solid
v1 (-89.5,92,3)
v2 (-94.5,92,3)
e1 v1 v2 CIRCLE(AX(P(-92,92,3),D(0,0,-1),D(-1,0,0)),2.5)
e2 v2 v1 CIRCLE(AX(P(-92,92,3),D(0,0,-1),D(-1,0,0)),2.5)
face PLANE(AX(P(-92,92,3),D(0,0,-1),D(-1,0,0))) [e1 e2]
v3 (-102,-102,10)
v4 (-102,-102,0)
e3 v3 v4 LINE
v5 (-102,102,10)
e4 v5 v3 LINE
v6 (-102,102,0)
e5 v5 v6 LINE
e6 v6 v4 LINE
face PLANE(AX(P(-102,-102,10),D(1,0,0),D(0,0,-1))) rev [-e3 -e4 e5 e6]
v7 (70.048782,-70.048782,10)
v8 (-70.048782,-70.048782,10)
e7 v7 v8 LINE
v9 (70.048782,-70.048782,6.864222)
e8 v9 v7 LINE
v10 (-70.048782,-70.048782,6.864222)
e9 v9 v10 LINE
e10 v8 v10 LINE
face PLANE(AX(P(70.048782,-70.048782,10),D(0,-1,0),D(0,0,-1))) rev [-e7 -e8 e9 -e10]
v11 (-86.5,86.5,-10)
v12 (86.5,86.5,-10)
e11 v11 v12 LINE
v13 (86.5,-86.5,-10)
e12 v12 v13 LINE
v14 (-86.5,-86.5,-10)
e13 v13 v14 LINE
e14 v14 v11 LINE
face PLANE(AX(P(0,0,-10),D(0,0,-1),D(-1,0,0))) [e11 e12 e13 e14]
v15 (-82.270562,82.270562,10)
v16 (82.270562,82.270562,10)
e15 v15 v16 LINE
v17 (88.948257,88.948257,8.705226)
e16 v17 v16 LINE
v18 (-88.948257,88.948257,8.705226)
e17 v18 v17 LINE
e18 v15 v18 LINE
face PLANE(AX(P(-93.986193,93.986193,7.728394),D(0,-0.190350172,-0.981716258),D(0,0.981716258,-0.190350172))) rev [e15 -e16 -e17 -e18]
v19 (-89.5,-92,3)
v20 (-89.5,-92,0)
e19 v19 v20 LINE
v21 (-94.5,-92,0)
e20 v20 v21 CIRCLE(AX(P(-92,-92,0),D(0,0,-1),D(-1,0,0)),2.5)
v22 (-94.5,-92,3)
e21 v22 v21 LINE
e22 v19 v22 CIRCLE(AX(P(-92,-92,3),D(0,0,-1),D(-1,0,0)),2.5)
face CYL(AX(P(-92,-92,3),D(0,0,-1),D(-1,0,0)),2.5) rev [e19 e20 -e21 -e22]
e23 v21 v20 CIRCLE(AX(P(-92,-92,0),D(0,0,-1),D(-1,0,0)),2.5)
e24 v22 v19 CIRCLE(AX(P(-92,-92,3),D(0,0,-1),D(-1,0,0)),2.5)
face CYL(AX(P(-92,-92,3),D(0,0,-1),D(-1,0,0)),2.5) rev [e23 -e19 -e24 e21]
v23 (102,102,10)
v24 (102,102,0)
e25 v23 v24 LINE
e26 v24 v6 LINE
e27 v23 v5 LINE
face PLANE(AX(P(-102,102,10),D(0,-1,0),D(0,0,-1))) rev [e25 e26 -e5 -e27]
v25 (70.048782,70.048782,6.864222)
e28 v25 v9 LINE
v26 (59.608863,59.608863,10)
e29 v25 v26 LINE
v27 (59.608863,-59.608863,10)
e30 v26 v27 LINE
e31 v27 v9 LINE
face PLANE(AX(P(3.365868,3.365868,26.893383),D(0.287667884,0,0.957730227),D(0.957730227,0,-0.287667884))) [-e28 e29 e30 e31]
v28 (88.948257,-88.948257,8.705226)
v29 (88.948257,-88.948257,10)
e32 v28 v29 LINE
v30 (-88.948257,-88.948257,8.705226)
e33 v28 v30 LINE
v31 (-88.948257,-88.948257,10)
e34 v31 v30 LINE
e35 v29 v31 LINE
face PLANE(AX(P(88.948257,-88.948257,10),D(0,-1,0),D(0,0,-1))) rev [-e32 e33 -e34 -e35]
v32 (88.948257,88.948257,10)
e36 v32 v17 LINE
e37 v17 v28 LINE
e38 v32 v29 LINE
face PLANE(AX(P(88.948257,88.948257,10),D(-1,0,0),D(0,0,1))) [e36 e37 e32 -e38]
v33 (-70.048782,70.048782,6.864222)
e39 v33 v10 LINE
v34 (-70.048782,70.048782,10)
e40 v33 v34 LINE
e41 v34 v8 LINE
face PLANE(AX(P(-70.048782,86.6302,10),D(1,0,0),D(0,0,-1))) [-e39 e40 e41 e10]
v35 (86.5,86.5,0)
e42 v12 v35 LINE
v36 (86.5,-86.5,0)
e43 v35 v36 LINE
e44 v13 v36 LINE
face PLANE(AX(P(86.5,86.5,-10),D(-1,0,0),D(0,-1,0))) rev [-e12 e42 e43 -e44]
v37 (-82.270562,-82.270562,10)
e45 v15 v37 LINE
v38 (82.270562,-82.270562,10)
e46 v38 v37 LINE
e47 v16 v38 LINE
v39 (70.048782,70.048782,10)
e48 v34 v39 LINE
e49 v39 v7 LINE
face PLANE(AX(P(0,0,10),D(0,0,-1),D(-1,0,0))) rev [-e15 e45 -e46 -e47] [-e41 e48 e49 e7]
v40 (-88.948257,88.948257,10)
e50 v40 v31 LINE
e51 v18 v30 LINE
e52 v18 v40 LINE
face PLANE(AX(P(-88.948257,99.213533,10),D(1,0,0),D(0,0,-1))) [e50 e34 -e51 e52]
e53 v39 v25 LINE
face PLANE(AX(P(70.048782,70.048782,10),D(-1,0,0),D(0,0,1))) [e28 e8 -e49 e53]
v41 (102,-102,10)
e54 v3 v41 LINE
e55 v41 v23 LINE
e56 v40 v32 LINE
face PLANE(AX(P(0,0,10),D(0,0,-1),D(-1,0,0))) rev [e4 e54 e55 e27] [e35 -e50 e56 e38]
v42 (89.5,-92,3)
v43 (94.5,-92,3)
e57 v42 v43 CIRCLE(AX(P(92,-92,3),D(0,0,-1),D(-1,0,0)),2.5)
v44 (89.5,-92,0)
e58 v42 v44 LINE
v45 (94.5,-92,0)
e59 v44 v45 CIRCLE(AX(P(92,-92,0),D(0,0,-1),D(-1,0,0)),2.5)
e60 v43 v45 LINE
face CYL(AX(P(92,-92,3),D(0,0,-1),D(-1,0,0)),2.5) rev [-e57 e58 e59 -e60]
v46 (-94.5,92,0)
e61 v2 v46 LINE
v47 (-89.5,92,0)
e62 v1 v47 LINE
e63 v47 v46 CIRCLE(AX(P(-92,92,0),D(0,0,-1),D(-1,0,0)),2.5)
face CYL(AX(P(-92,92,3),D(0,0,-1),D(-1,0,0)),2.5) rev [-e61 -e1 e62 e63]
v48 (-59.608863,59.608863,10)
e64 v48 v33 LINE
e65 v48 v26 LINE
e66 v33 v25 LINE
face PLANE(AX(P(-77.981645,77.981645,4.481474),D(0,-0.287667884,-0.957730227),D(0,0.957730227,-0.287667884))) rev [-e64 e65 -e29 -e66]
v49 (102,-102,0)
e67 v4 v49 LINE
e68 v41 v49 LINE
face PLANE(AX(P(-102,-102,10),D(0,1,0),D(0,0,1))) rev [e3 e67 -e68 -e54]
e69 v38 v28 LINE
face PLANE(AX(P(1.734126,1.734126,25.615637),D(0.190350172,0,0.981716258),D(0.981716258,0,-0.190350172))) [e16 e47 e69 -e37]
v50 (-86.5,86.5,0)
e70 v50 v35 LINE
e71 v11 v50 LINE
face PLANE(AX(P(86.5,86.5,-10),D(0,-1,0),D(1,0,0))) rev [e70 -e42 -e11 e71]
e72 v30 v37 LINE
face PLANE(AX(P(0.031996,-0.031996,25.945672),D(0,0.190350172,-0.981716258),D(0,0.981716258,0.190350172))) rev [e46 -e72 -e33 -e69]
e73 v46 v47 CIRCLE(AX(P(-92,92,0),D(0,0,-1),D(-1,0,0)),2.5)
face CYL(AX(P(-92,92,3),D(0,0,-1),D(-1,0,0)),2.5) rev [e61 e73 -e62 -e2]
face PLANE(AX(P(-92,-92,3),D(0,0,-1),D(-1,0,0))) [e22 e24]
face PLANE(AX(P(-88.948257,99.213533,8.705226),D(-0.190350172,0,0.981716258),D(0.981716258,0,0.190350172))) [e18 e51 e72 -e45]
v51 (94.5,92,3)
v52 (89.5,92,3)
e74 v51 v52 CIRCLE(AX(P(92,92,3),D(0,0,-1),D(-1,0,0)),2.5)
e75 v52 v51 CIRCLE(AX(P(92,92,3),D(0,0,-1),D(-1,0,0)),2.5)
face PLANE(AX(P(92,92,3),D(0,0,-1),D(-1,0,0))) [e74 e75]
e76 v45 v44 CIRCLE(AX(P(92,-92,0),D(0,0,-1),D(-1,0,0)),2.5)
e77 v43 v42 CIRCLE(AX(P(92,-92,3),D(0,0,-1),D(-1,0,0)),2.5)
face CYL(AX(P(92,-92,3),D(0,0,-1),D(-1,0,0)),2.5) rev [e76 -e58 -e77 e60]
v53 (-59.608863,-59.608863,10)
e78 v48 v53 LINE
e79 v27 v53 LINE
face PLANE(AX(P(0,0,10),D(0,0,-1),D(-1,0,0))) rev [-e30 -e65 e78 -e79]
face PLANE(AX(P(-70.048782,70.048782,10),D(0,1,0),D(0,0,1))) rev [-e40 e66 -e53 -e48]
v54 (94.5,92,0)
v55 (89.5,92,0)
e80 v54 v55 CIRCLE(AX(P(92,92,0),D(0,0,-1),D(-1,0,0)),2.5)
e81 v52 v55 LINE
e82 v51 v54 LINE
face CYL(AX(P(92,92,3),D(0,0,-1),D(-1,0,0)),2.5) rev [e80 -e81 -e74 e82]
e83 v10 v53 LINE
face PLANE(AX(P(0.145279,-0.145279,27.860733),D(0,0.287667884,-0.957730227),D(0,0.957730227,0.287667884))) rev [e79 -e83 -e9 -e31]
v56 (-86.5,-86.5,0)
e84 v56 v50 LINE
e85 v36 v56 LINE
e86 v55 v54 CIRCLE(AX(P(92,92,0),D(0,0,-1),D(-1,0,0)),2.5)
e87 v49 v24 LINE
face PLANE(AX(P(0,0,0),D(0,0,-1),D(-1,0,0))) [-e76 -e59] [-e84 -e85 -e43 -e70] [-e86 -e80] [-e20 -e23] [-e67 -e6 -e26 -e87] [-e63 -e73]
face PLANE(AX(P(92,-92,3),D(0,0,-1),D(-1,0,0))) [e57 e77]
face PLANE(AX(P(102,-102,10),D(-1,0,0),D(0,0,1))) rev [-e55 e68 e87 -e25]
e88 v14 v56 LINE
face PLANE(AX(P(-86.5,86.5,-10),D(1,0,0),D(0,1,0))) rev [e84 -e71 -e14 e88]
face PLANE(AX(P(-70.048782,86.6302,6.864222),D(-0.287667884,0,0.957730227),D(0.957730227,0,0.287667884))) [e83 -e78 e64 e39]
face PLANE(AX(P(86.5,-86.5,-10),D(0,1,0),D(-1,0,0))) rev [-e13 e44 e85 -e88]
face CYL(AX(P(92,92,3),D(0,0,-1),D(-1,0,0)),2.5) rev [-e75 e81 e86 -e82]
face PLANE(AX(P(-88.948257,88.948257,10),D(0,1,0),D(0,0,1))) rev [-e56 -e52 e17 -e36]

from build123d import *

# Parameters (mm, degrees)
SKETCH_1_W          = 204
SKETCH_1_H          = 204
EXTRUDE_1_DEPTH     = 10
SKETCH_6_R          = 2.5
CUT_EXTRUDE_1_DEPTH = 3
SKETCH_7_W          = 173
SKETCH_7_H          = 173
EXTRUDE_2_DEPTH     = 10


with BuildPart() as part:
    # 草图1 → 凸台-拉伸1 (new body)
    with BuildSketch(Plane.XY):
        Rectangle(SKETCH_1_W, SKETCH_1_H)
    extrude(amount=EXTRUDE_1_DEPTH)

    # 切除-扫描2: sweep along a path in 草图2
    with BuildLine(Plane.XY.offset(10)) as sweep_2_path:
        Line((-80, -80), (80, -80))
        Line((80, -80), (80, 80))
        Line((80, 80), (-80, 80))
        Line((-80, 80), (-80, -80))
    # 草图3 → 切除-扫描2 (sweep, cut)
    with BuildSketch(Plane(origin=(0, 0, 0), x_dir=(1, 0, 0), z_dir=(0, 1, 0))):
        Polygon((-88.948256764, -10), (-88.948256764, -8.70522639), (-82.270562222, -10), align=None)
    sweep(path=sweep_2_path.line, transition=Transition.RIGHT, mode=Mode.SUBTRACT)

    # 切除-扫描3: sweep along a path in 草图4
    with BuildLine(Plane.XY.offset(10)) as sweep_3_path:
        Line((-70, -70), (70, -70))
        Line((70, -70), (70, 70))
        Line((70, 70), (-70, 70))
        Line((-70, 70), (-70, -70))
    # 草图5 → 切除-扫描3 (sweep, cut)
    with BuildSketch(Plane(origin=(0, 0, 0), x_dir=(1, 0, 0), z_dir=(0, 1, 0))):
        Polygon((-70.048782141, -10), (-70.048782141, -6.864221928), (-59.608863027, -10), align=None)
    sweep(path=sweep_3_path.line, transition=Transition.RIGHT, mode=Mode.SUBTRACT)

    # 草图6 → 切除-拉伸1 (cut)
    with BuildSketch(Plane(origin=(0, 0, 0), x_dir=(-1, 0, 0), z_dir=(0, 0, -1))):
        with Locations((-92, 92)):
            Circle(SKETCH_6_R)
        with Locations((92, 92)):
            Circle(SKETCH_6_R)
        with Locations((-92, -92)):
            Circle(SKETCH_6_R)
        with Locations((92, -92)):
            Circle(SKETCH_6_R)
    extrude(amount=-CUT_EXTRUDE_1_DEPTH, mode=Mode.SUBTRACT)

    # 草图7 → 凸台-拉伸2 (add)
    with BuildSketch(Plane(origin=(0, 0, 0), x_dir=(-1, 0, 0), z_dir=(0, 0, -1))):
        Rectangle(SKETCH_7_W, SKETCH_7_H)
    extrude(amount=EXTRUDE_2_DEPTH)


solid = part.part
